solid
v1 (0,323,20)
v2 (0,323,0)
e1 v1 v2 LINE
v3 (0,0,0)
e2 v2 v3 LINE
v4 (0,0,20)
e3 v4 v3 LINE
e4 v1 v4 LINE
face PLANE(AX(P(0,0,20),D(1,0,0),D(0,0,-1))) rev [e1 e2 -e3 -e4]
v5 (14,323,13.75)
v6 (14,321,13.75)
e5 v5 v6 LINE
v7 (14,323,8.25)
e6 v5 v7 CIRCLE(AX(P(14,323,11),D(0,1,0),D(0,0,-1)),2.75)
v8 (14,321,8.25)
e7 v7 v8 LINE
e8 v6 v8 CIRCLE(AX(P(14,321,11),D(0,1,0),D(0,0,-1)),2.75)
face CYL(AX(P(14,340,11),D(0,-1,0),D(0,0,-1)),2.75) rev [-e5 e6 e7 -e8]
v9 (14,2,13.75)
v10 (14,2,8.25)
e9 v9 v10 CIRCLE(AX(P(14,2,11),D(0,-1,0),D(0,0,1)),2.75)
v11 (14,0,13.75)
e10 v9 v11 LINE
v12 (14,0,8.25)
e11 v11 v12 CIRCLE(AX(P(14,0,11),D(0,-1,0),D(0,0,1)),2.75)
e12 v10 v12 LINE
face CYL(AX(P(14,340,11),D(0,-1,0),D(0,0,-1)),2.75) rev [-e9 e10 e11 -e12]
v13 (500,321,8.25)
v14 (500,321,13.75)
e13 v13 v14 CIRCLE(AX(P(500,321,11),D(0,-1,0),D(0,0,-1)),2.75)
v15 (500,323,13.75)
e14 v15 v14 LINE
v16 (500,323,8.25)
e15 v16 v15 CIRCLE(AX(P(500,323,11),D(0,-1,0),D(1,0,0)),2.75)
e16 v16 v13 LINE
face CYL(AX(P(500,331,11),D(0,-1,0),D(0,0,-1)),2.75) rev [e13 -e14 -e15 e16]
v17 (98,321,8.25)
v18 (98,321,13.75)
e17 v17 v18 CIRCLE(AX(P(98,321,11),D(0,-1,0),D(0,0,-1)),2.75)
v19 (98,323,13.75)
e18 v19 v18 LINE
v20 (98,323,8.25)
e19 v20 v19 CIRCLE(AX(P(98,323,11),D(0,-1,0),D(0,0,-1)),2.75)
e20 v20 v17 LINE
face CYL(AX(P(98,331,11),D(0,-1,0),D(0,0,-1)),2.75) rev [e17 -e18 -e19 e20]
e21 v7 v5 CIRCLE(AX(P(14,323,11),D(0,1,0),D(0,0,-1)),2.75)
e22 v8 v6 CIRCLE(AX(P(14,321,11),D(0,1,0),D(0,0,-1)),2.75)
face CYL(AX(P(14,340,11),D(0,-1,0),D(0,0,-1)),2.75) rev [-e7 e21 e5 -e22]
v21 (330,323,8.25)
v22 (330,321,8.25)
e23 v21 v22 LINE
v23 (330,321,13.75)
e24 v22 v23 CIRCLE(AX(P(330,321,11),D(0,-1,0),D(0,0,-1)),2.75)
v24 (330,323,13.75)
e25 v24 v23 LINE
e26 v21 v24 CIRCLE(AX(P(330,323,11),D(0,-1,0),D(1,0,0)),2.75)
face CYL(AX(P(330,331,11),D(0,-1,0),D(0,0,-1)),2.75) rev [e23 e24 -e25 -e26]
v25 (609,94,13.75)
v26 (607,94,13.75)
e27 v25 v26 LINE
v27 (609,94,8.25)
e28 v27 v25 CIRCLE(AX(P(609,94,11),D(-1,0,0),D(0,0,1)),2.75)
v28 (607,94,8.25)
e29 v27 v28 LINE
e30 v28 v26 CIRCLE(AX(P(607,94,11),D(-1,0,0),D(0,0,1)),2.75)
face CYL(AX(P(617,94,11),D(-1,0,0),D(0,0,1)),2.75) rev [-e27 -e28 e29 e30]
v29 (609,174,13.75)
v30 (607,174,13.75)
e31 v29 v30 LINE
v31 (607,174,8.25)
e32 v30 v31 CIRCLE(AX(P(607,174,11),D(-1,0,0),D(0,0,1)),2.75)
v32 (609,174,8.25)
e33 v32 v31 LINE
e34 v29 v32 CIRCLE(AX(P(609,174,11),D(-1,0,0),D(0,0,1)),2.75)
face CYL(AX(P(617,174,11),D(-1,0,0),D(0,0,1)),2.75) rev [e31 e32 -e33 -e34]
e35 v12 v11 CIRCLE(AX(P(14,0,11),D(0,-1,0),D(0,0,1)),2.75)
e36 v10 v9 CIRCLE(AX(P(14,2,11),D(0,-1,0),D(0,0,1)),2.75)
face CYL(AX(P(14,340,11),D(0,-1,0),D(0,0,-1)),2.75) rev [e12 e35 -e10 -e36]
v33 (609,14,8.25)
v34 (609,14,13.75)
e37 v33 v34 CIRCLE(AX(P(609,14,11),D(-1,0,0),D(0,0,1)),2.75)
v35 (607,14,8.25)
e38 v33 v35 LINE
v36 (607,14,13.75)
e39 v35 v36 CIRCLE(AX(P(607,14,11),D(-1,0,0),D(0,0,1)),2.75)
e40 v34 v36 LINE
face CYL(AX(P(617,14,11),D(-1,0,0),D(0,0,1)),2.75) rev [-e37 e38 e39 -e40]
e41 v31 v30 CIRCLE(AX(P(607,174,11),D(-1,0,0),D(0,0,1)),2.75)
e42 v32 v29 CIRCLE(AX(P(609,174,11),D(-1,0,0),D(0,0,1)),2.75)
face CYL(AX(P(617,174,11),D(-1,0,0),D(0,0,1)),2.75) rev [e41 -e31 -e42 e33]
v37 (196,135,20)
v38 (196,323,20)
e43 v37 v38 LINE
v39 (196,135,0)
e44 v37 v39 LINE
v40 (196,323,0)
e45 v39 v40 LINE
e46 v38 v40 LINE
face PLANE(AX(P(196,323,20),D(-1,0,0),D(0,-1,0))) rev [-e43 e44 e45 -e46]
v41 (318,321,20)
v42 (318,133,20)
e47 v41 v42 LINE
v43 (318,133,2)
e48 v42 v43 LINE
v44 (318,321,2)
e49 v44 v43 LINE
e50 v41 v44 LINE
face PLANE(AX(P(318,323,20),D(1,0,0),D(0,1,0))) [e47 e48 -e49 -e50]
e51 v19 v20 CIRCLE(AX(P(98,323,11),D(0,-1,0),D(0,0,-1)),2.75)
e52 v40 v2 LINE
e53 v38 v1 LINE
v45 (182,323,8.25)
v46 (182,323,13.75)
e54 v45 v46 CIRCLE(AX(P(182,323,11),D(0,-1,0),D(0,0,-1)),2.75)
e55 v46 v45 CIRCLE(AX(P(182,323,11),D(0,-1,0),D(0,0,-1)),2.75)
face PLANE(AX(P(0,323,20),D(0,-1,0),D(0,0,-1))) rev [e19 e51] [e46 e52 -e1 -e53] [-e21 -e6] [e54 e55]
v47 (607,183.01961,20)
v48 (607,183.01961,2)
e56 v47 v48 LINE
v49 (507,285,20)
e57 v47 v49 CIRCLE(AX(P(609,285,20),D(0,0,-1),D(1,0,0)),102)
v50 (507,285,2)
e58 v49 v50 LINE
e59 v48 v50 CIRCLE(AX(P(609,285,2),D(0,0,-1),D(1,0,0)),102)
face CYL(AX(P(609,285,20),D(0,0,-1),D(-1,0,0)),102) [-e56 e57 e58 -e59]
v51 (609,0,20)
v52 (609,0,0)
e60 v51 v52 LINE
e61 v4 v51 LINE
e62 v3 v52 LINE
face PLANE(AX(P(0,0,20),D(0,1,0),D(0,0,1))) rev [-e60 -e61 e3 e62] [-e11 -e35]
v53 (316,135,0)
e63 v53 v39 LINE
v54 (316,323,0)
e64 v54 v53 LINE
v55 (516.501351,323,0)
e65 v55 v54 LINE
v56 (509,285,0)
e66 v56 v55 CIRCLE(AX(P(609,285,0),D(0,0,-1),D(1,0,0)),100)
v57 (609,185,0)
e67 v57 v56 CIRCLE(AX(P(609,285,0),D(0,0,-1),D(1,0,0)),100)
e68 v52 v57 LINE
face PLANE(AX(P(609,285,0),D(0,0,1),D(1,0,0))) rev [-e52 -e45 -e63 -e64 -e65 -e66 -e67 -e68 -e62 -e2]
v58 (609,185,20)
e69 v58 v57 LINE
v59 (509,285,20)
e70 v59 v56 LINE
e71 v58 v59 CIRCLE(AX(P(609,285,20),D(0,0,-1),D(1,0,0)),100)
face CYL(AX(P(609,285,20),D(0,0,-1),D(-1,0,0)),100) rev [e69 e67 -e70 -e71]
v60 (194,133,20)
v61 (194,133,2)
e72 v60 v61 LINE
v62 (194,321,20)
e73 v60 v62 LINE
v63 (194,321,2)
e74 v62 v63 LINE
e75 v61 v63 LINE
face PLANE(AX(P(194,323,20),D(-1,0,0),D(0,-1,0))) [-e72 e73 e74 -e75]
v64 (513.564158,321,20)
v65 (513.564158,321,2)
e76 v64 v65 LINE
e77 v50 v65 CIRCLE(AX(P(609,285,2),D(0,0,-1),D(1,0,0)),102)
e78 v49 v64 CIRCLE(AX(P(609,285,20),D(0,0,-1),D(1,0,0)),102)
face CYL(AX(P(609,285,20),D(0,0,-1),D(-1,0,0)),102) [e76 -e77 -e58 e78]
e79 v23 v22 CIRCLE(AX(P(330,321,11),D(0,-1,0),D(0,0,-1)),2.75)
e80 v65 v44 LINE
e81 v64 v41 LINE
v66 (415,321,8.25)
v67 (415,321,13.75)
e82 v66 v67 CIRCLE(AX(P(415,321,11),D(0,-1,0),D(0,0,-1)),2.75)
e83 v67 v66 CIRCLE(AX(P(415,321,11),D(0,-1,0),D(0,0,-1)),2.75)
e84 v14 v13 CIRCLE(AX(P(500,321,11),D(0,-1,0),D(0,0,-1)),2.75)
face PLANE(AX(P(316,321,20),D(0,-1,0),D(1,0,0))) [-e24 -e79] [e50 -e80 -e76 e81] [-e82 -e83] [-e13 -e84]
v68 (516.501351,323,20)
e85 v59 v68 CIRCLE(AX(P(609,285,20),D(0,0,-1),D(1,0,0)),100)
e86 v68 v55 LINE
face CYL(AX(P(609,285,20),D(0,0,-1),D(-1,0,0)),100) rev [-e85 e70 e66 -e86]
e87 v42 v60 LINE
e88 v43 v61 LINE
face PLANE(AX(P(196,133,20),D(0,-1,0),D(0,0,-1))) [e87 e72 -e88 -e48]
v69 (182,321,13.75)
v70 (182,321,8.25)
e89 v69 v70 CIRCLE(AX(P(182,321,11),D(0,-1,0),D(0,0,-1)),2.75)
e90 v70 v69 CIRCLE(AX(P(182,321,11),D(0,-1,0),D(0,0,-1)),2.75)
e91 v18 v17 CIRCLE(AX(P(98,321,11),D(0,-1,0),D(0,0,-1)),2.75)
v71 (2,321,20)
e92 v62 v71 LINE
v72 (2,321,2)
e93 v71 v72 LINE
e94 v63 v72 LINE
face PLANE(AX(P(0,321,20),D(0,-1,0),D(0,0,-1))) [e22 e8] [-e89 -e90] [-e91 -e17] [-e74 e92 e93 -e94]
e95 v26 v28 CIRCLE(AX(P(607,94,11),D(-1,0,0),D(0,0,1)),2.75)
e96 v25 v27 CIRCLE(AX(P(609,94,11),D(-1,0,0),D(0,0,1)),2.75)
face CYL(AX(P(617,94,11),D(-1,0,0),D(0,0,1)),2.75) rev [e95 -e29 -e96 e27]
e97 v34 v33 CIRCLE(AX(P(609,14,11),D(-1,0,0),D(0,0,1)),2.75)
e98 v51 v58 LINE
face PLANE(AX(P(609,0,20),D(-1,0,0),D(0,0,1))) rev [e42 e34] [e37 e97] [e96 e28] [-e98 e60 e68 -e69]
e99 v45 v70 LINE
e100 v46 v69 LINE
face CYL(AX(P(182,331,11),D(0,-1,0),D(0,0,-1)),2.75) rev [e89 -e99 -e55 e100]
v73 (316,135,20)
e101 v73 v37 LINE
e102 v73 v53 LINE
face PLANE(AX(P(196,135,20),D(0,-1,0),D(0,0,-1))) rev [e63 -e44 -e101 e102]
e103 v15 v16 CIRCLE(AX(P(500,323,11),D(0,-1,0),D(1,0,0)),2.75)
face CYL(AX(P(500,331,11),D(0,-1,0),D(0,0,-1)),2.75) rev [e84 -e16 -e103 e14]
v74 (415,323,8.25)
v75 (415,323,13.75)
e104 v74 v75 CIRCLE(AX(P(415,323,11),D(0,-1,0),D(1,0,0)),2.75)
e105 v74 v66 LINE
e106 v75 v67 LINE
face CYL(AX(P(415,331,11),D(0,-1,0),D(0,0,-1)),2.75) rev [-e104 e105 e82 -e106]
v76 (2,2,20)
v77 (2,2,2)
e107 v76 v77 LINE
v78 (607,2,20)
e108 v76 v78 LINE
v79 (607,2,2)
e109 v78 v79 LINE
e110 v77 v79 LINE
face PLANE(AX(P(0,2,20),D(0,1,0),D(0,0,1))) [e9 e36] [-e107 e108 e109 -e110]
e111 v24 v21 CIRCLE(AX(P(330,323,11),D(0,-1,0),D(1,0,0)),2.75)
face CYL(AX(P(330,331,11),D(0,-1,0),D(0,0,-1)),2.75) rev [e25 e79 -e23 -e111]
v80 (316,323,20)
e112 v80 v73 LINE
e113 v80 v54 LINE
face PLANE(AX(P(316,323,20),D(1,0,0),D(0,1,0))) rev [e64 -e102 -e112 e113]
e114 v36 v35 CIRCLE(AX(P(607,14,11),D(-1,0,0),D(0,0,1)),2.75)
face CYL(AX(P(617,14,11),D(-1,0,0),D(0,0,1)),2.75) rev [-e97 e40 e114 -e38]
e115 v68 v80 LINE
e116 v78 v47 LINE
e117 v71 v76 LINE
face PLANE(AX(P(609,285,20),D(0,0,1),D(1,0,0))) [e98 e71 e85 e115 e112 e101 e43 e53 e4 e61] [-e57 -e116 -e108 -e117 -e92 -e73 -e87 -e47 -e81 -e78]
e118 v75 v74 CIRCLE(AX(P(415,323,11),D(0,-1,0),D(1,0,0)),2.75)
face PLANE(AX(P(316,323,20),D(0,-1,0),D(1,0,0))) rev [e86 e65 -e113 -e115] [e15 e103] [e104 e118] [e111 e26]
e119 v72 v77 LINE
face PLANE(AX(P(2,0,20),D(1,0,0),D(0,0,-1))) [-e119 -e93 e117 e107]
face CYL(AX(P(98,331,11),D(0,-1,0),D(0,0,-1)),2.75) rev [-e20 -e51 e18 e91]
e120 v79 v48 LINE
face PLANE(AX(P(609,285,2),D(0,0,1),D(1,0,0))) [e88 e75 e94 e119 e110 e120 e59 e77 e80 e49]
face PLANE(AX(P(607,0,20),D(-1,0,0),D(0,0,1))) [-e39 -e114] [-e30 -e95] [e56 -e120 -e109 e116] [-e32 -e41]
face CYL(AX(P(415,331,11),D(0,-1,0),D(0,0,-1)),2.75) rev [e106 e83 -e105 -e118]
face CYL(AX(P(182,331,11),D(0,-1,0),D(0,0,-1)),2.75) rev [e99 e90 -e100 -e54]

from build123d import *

# Parameters (mm, degrees)
EXTRUDE_1_DEPTH          = 20
SHELL_1_T                = -2
CUT_EXTRUDE_1_DEPTH      = 338
CUT_EXTRUDE_1_DEPTH_BACK = 10
SKETCH_2_R               = 2.75
SKETCH_3_R               = 2.75
CUT_EXTRUDE_2_DEPTH      = 10
SKETCH_4_R               = 2.75
CUT_EXTRUDE_3_DEPTH      = 10


with BuildPart() as part:
    # 草图1 → 凸台-拉伸1 (new body)
    with BuildSketch(Plane.XY):
        with BuildLine():
            Line((0, 0), (609, 0))
            Line((609, 0), (609, 185))
            ThreePointArc((609, 185), (525.933761371, 229.322356372), (516.501351361, 323))
            Line((516.501351361, 323), (316, 323))
            Line((316, 323), (316, 135))
            Line((316, 135), (196, 135))
            Line((196, 135), (196, 323))
            Line((196, 323), (0, 323))
            Line((0, 323), (0, 0))
        make_face()
    extrude(amount=EXTRUDE_1_DEPTH)

    # 抽壳1
    shell_1_openings = [part.faces().sort_by_distance(p)[0] for p in [
        (304.5, 6.893547708, 20),
    ]]
    offset(amount=SHELL_1_T, openings=shell_1_openings, kind=Kind.INTERSECTION)

    # 草图2 → 切除-拉伸1 (cut, two sides: drawn at the far end of the back side and taken through both)
    with BuildSketch(Plane(origin=(0, 2, 0), x_dir=(1, 0, 0), z_dir=(0, 1, 0)).offset(-CUT_EXTRUDE_1_DEPTH_BACK)):
        with Locations(Location((14, -11, 0), (0, 0, 90))):
            Circle(SKETCH_2_R)
    extrude(amount=CUT_EXTRUDE_1_DEPTH + CUT_EXTRUDE_1_DEPTH_BACK, mode=Mode.SUBTRACT)

    # 草图3 → 切除-拉伸2 (cut)
    with BuildSketch(Plane.XZ.offset(-321)):
        with Locations(Location((98, 11, 0), (0, 0, 270))):
            Circle(SKETCH_3_R)
        with Locations(Location((182, 11, 0), (0, 0, 270))):
            Circle(SKETCH_3_R)
        with Locations(Location((330, 11, 0), (0, 0, 270))):
            Circle(SKETCH_3_R)
        with Locations(Location((415, 11, 0), (0, 0, 270))):
            Circle(SKETCH_3_R)
        with Locations(Location((500, 11, 0), (0, 0, 270))):
            Circle(SKETCH_3_R)
    extrude(amount=-CUT_EXTRUDE_2_DEPTH, mode=Mode.SUBTRACT)

    # 草图4 → 切除-拉伸3 (cut)
    with BuildSketch(Plane.ZY.offset(-607)):
        with Locations((11, 14)):
            Circle(SKETCH_4_R)
        with Locations((11, 94)):
            Circle(SKETCH_4_R)
        with Locations((11, 174)):
            Circle(SKETCH_4_R)
    extrude(amount=-CUT_EXTRUDE_3_DEPTH, mode=Mode.SUBTRACT)


solid = part.part
